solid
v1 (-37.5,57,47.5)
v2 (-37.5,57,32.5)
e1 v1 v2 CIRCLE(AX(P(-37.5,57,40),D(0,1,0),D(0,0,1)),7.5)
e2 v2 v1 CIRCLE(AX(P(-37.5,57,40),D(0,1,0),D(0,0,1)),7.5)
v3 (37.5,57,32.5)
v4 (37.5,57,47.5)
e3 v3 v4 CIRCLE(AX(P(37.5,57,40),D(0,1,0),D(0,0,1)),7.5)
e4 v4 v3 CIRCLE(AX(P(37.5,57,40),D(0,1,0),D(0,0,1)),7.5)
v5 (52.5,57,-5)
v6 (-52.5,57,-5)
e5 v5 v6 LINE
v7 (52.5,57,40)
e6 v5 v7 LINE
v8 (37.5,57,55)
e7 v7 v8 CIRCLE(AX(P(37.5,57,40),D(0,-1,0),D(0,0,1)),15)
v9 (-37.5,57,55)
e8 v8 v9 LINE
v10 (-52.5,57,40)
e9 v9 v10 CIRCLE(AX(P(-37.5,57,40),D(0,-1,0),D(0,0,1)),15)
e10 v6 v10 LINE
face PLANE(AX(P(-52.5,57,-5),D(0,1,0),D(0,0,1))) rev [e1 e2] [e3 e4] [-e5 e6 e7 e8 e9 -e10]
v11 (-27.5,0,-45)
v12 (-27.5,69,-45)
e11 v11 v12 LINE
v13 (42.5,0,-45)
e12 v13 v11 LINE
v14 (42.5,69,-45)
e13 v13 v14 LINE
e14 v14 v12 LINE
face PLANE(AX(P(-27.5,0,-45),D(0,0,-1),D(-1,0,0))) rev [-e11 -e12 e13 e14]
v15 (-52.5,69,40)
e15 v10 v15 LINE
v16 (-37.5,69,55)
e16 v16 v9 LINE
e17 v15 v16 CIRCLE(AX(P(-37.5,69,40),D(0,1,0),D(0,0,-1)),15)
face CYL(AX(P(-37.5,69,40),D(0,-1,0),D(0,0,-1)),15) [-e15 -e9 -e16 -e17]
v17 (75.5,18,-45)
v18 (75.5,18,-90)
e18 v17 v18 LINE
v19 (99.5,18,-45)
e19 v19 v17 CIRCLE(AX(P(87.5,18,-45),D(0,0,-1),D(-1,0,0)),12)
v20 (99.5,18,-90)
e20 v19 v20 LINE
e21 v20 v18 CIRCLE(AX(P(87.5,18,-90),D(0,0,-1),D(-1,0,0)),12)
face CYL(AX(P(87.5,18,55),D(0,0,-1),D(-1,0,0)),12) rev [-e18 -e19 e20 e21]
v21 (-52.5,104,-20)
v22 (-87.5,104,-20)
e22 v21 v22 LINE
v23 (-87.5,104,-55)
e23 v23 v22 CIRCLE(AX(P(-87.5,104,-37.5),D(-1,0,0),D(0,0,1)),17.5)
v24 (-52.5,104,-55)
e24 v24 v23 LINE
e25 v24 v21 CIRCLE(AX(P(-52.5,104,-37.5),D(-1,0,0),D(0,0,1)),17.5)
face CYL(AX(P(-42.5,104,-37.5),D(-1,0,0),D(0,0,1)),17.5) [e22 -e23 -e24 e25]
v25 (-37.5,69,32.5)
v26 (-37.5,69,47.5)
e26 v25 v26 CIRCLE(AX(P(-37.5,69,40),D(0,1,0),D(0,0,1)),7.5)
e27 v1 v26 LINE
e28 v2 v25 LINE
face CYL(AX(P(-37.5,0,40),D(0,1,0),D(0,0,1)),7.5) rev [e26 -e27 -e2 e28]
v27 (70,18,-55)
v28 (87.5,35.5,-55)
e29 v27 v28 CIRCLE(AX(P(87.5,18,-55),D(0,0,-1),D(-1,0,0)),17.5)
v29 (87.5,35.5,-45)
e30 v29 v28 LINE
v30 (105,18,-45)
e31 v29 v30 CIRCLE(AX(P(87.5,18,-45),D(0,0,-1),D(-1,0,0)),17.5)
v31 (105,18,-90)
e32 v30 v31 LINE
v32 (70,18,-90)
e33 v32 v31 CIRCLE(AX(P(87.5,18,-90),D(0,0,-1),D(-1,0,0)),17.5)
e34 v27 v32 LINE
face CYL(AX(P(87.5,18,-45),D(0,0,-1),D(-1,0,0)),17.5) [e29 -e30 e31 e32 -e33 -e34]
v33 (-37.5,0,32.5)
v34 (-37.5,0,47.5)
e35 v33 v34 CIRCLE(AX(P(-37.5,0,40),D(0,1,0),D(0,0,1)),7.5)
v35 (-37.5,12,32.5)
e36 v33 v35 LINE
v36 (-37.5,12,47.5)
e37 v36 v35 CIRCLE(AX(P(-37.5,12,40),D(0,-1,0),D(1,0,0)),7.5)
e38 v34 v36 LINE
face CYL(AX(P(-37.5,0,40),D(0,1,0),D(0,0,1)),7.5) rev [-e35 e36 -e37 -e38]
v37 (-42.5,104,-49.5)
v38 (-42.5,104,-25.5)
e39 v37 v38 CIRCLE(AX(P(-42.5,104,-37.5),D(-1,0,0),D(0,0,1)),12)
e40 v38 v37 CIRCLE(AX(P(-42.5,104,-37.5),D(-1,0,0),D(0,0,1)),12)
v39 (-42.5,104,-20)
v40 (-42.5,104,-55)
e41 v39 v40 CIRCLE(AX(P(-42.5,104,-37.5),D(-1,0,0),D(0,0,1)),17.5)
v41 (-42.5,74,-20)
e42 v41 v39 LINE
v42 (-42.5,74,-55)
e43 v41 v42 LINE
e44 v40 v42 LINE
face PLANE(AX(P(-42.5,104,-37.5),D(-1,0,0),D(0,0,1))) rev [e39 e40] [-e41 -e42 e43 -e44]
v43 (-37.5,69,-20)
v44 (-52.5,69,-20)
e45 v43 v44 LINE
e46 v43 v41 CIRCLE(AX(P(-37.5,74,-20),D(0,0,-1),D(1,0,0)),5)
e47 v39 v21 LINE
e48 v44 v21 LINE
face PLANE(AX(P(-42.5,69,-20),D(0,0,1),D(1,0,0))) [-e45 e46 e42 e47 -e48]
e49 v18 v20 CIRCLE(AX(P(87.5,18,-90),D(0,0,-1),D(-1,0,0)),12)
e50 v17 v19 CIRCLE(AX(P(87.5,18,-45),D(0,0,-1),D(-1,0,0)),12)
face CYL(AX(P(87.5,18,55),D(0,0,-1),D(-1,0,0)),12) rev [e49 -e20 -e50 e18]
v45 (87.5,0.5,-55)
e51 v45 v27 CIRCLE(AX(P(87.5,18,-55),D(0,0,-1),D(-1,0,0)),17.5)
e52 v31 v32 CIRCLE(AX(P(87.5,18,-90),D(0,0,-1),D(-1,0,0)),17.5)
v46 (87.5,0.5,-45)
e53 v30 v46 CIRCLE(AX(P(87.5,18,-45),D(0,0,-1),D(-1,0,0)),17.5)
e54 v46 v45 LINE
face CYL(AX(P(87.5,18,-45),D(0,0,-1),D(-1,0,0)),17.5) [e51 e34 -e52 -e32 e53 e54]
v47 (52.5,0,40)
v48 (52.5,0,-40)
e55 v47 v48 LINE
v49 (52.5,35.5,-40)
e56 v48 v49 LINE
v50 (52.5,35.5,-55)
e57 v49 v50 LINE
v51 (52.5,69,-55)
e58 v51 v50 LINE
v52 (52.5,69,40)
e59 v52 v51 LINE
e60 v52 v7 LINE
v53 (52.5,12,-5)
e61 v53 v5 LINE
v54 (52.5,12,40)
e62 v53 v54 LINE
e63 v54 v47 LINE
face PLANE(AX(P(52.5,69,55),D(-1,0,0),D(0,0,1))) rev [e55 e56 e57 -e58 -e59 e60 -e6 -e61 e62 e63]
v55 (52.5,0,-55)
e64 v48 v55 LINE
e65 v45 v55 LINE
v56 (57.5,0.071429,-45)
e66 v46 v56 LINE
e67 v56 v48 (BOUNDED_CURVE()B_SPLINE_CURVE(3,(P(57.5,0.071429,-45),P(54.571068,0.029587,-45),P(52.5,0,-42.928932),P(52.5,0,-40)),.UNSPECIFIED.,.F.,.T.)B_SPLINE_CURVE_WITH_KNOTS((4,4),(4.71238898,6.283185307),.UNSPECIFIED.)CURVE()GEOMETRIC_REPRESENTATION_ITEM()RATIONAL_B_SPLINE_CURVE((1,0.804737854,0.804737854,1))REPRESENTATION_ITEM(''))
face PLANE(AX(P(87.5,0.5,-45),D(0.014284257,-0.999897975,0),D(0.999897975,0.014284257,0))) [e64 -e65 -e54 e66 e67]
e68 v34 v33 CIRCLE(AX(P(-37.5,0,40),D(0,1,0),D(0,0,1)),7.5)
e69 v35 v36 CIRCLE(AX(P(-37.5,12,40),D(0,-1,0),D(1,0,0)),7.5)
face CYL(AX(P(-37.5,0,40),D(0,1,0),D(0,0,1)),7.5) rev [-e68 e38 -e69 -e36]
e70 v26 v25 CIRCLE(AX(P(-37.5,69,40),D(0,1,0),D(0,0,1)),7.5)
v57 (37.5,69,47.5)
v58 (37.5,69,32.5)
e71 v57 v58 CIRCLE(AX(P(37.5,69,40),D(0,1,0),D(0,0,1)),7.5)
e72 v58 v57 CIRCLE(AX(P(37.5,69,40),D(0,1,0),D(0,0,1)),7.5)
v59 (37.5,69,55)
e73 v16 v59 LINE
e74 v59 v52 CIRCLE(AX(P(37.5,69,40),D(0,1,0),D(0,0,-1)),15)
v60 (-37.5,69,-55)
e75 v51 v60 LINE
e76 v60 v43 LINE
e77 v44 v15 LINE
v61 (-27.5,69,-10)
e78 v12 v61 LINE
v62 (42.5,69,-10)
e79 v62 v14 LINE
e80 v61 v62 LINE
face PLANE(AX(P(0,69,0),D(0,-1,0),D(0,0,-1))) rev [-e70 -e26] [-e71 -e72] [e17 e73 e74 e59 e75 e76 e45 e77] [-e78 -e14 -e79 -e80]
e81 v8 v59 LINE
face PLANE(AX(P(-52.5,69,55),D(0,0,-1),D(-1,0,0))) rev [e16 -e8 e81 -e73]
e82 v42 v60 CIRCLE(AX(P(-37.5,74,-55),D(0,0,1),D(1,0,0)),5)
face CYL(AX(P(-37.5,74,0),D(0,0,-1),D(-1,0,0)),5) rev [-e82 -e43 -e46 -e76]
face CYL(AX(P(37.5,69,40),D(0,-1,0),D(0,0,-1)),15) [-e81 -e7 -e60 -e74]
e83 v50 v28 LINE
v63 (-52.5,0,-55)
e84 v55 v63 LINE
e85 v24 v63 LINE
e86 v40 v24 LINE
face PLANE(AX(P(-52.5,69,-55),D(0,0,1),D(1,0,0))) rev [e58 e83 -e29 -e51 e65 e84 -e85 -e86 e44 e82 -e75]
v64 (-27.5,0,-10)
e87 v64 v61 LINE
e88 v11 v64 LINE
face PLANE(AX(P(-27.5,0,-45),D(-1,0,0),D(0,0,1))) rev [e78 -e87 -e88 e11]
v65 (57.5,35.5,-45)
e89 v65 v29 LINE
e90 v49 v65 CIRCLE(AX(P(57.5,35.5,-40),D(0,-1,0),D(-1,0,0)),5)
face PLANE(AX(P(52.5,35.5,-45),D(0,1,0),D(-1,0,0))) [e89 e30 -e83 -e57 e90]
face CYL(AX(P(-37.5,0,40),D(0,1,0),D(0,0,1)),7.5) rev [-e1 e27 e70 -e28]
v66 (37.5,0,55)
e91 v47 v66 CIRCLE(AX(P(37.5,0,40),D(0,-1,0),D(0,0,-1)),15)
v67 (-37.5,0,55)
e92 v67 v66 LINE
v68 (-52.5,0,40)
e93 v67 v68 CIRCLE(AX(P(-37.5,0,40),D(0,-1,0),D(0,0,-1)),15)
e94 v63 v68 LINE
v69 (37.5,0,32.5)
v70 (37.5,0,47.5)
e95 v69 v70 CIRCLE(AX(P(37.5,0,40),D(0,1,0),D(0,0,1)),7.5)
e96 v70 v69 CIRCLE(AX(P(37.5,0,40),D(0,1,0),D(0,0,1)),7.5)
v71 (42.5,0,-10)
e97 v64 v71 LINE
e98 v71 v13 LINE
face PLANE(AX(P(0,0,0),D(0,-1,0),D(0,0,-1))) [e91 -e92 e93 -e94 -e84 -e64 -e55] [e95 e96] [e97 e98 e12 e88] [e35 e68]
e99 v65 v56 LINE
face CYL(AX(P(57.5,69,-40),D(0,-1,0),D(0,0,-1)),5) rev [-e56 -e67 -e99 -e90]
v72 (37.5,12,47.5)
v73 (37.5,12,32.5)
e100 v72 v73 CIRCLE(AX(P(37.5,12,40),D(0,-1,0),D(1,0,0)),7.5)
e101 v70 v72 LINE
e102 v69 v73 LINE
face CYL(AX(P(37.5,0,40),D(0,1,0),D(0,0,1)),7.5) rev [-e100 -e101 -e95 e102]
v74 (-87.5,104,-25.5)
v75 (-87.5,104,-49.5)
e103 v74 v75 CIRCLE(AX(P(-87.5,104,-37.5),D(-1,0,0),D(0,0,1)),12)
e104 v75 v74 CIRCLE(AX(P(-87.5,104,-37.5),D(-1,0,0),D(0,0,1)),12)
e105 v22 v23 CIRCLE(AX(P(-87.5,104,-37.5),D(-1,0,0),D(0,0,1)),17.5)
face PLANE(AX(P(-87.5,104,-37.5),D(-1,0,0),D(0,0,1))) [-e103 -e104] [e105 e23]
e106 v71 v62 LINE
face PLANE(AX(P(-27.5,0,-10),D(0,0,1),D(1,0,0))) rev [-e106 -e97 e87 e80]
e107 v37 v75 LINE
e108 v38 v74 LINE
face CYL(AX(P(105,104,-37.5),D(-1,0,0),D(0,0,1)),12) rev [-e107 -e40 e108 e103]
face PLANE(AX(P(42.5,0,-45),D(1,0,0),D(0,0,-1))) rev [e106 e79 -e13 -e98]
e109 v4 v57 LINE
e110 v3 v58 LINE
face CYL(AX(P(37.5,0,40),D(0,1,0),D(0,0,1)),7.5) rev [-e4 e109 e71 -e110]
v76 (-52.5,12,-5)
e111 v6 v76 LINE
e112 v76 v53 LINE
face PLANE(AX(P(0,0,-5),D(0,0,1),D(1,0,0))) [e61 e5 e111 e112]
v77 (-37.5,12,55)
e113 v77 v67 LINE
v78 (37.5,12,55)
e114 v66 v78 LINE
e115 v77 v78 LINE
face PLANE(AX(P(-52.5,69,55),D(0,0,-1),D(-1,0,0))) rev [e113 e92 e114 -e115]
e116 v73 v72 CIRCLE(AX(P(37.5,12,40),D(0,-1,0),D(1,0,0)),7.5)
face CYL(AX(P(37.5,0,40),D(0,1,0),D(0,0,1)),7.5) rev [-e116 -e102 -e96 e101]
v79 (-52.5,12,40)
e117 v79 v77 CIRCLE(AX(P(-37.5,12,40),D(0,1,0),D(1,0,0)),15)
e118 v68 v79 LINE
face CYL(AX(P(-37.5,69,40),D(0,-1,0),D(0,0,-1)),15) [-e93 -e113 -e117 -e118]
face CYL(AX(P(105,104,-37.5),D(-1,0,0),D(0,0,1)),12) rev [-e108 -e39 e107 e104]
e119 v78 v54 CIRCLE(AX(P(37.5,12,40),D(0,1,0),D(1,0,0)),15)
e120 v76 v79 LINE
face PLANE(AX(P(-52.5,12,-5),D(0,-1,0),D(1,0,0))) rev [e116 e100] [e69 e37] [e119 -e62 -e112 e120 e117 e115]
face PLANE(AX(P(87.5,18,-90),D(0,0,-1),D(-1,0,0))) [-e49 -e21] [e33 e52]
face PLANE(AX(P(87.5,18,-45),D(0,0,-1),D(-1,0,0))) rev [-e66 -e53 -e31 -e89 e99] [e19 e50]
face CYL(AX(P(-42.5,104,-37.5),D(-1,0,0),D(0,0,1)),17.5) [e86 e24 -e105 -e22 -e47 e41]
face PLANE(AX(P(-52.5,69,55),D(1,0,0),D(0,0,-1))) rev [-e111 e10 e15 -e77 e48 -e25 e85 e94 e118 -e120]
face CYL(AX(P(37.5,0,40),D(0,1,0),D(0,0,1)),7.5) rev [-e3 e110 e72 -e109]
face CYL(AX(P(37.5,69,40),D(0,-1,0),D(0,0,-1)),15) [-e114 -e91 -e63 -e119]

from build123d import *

# Parameters (mm, degrees)
BASE_BLOCK_PROFILE_W        = 105
BASE_BLOCK_PROFILE_H        = 110
BASE_BLOCK_DEPTH            = 69
FORK_SLOT_PROFILE_W         = 105
FORK_SLOT_PROFILE_H         = 45
FORK_SLOT_CUT_DEPTH         = 60
FLANGE_CORNER_FILLETS_R15_R = 15
FLANGE_HOLES_PROFILE_R      = 7.5
FLANGE_HOLES_DEPTH          = 103.67545958
TOP_WINDOW_PROFILE_W        = 70
TOP_WINDOW_PROFILE_H        = 35
TOP_WINDOW_CUT_35X25_DEPTH  = 103.67545958
LUG_PLATE_A_DEPTH           = 10
LUG_START                   = 35
LUG_BOSS_A_PROFILE_R        = 17.5
LUG_BOSS_A_35_DEPTH         = 35
LUG_BORE_A_PROFILE_R        = 12
LUG_BORE_A_24_DEPTH         = 192.861929522
LUG_PLATE_B_DEPTH           = 10
LUG_BOSS_B_PROFILE_R        = 17.5
LUG_BOSS_B_35_DEPTH         = 35
LUG_BORE_B_PROFILE_R        = 12
LUG_BORE_B_24_DEPTH         = 245.782556568
LUG_BLEND_FILLETS_R5_R      = 5


with BuildPart() as part:
    # Base Block Profile → Base Block (new body)
    with BuildSketch(Plane(origin=(0, 0, 0), x_dir=(1, 0, 0), z_dir=(0, 1, 0))):
        Rectangle(BASE_BLOCK_PROFILE_W, BASE_BLOCK_PROFILE_H)
    extrude(amount=BASE_BLOCK_DEPTH)

    # Fork Slot Profile → Fork Slot Cut (cut)
    with BuildSketch(Plane.XY.offset(55)):
        with Locations((0, 34.5)):
            Rectangle(FORK_SLOT_PROFILE_W, FORK_SLOT_PROFILE_H)
    extrude(amount=-FORK_SLOT_CUT_DEPTH, mode=Mode.SUBTRACT)

    # Flange Corner Fillets R15
    flange_corner_fillets_r15_edges = [part.edges().sort_by_distance(p)[0] for p in [
        (52.5, 6, 55),
        (-52.5, 6, 55),
        (52.5, 63, 55),
        (-52.5, 63, 55),
    ]]
    fillet(flange_corner_fillets_r15_edges, radius=FLANGE_CORNER_FILLETS_R15_R)

    # Flange Holes Profile → Flange Holes (cut, through all)
    with BuildSketch(Plane(origin=(0, 69, 0), x_dir=(1, 0, 0), z_dir=(0, 1, 0))):
        with Locations(Location((-37.5, -40, 0), (0, 0, 270))):
            Circle(FLANGE_HOLES_PROFILE_R)
        with Locations(Location((37.5, -40, 0), (0, 0, 270))):
            Circle(FLANGE_HOLES_PROFILE_R)
    extrude(amount=-FLANGE_HOLES_DEPTH, mode=Mode.SUBTRACT)

    # Top Window Profile → Top Window Cut 35x25 (cut, through all)
    with BuildSketch(Plane(origin=(0, 69, 0), x_dir=(1, 0, 0), z_dir=(0, 1, 0))):
        with Locations((7.5, 27.5)):
            Rectangle(TOP_WINDOW_PROFILE_W, TOP_WINDOW_PROFILE_H)
    extrude(amount=-TOP_WINDOW_CUT_35X25_DEPTH, mode=Mode.SUBTRACT)

    # Lug Plate A Profile → Lug Plate A (add)
    with BuildSketch(Plane(origin=(0, 0, -55), x_dir=(-1, 0, 0), z_dir=(0, 0, -1))):
        with BuildLine():
            Line((-87.5, 0.5), (-52.5, 0))
            Line((-52.5, 0), (-52.5, 35.5))
            Line((-52.5, 35.5), (-87.5, 35.5))
            ThreePointArc((-87.5, 35.5), (-105, 18), (-87.5, 0.5))
        make_face()
    extrude(amount=-LUG_PLATE_A_DEPTH)

    # Lug Boss A Profile → Lug Boss A _35 (add)
    with BuildSketch(Plane(origin=(0, 0, -55), x_dir=(-1, 0, 0), z_dir=(0, 0, -1)).offset(LUG_START)):
        with Locations((-87.5, 18)):
            Circle(LUG_BOSS_A_PROFILE_R)
    extrude(amount=-LUG_BOSS_A_35_DEPTH)

    # Lug Bore A Profile → Lug Bore A _24 (cut, through all)
    with BuildSketch(Plane(origin=(0, 0, -90), x_dir=(-1, 0, 0), z_dir=(0, 0, -1))):
        with Locations((-87.5, 18)):
            Circle(LUG_BORE_A_PROFILE_R)
    extrude(amount=-LUG_BORE_A_24_DEPTH, mode=Mode.SUBTRACT)

    # Lug Plate B Profile → Lug Plate B (add)
    with BuildSketch(Plane.ZY.offset(52.5)):
        with BuildLine():
            Line((-55, 104), (-55, 69))
            Line((-55, 69), (-20, 69))
            Line((-20, 69), (-20, 104))
            ThreePointArc((-20, 104), (-37.5, 121.5), (-55, 104))
        make_face()
    extrude(amount=-LUG_PLATE_B_DEPTH)

    # Lug Boss B Profile → Lug Boss B _35 (add)
    with BuildSketch(Plane.ZY.offset(52.5).offset(LUG_START)):
        with Locations((-37.5, 104)):
            Circle(LUG_BOSS_B_PROFILE_R)
    extrude(amount=-LUG_BOSS_B_35_DEPTH)

    # Lug Bore B Profile → Lug Bore B _24 (cut, through all)
    with BuildSketch(Plane.ZY.offset(87.5)):
        with Locations((-37.5, 104)):
            Circle(LUG_BORE_B_PROFILE_R)
    extrude(amount=-LUG_BORE_B_24_DEPTH, mode=Mode.SUBTRACT)

    # Lug Blend Fillets R5
    lug_blend_fillets_r5_edges = [part.edges().sort_by_distance(p)[0] for p in [
        (-42.5, 69, -37.5),
        (52.5, 17.75, -45),
    ]]
    fillet(lug_blend_fillets_r5_edges, radius=LUG_BLEND_FILLETS_R5_R)


solid = part.part
